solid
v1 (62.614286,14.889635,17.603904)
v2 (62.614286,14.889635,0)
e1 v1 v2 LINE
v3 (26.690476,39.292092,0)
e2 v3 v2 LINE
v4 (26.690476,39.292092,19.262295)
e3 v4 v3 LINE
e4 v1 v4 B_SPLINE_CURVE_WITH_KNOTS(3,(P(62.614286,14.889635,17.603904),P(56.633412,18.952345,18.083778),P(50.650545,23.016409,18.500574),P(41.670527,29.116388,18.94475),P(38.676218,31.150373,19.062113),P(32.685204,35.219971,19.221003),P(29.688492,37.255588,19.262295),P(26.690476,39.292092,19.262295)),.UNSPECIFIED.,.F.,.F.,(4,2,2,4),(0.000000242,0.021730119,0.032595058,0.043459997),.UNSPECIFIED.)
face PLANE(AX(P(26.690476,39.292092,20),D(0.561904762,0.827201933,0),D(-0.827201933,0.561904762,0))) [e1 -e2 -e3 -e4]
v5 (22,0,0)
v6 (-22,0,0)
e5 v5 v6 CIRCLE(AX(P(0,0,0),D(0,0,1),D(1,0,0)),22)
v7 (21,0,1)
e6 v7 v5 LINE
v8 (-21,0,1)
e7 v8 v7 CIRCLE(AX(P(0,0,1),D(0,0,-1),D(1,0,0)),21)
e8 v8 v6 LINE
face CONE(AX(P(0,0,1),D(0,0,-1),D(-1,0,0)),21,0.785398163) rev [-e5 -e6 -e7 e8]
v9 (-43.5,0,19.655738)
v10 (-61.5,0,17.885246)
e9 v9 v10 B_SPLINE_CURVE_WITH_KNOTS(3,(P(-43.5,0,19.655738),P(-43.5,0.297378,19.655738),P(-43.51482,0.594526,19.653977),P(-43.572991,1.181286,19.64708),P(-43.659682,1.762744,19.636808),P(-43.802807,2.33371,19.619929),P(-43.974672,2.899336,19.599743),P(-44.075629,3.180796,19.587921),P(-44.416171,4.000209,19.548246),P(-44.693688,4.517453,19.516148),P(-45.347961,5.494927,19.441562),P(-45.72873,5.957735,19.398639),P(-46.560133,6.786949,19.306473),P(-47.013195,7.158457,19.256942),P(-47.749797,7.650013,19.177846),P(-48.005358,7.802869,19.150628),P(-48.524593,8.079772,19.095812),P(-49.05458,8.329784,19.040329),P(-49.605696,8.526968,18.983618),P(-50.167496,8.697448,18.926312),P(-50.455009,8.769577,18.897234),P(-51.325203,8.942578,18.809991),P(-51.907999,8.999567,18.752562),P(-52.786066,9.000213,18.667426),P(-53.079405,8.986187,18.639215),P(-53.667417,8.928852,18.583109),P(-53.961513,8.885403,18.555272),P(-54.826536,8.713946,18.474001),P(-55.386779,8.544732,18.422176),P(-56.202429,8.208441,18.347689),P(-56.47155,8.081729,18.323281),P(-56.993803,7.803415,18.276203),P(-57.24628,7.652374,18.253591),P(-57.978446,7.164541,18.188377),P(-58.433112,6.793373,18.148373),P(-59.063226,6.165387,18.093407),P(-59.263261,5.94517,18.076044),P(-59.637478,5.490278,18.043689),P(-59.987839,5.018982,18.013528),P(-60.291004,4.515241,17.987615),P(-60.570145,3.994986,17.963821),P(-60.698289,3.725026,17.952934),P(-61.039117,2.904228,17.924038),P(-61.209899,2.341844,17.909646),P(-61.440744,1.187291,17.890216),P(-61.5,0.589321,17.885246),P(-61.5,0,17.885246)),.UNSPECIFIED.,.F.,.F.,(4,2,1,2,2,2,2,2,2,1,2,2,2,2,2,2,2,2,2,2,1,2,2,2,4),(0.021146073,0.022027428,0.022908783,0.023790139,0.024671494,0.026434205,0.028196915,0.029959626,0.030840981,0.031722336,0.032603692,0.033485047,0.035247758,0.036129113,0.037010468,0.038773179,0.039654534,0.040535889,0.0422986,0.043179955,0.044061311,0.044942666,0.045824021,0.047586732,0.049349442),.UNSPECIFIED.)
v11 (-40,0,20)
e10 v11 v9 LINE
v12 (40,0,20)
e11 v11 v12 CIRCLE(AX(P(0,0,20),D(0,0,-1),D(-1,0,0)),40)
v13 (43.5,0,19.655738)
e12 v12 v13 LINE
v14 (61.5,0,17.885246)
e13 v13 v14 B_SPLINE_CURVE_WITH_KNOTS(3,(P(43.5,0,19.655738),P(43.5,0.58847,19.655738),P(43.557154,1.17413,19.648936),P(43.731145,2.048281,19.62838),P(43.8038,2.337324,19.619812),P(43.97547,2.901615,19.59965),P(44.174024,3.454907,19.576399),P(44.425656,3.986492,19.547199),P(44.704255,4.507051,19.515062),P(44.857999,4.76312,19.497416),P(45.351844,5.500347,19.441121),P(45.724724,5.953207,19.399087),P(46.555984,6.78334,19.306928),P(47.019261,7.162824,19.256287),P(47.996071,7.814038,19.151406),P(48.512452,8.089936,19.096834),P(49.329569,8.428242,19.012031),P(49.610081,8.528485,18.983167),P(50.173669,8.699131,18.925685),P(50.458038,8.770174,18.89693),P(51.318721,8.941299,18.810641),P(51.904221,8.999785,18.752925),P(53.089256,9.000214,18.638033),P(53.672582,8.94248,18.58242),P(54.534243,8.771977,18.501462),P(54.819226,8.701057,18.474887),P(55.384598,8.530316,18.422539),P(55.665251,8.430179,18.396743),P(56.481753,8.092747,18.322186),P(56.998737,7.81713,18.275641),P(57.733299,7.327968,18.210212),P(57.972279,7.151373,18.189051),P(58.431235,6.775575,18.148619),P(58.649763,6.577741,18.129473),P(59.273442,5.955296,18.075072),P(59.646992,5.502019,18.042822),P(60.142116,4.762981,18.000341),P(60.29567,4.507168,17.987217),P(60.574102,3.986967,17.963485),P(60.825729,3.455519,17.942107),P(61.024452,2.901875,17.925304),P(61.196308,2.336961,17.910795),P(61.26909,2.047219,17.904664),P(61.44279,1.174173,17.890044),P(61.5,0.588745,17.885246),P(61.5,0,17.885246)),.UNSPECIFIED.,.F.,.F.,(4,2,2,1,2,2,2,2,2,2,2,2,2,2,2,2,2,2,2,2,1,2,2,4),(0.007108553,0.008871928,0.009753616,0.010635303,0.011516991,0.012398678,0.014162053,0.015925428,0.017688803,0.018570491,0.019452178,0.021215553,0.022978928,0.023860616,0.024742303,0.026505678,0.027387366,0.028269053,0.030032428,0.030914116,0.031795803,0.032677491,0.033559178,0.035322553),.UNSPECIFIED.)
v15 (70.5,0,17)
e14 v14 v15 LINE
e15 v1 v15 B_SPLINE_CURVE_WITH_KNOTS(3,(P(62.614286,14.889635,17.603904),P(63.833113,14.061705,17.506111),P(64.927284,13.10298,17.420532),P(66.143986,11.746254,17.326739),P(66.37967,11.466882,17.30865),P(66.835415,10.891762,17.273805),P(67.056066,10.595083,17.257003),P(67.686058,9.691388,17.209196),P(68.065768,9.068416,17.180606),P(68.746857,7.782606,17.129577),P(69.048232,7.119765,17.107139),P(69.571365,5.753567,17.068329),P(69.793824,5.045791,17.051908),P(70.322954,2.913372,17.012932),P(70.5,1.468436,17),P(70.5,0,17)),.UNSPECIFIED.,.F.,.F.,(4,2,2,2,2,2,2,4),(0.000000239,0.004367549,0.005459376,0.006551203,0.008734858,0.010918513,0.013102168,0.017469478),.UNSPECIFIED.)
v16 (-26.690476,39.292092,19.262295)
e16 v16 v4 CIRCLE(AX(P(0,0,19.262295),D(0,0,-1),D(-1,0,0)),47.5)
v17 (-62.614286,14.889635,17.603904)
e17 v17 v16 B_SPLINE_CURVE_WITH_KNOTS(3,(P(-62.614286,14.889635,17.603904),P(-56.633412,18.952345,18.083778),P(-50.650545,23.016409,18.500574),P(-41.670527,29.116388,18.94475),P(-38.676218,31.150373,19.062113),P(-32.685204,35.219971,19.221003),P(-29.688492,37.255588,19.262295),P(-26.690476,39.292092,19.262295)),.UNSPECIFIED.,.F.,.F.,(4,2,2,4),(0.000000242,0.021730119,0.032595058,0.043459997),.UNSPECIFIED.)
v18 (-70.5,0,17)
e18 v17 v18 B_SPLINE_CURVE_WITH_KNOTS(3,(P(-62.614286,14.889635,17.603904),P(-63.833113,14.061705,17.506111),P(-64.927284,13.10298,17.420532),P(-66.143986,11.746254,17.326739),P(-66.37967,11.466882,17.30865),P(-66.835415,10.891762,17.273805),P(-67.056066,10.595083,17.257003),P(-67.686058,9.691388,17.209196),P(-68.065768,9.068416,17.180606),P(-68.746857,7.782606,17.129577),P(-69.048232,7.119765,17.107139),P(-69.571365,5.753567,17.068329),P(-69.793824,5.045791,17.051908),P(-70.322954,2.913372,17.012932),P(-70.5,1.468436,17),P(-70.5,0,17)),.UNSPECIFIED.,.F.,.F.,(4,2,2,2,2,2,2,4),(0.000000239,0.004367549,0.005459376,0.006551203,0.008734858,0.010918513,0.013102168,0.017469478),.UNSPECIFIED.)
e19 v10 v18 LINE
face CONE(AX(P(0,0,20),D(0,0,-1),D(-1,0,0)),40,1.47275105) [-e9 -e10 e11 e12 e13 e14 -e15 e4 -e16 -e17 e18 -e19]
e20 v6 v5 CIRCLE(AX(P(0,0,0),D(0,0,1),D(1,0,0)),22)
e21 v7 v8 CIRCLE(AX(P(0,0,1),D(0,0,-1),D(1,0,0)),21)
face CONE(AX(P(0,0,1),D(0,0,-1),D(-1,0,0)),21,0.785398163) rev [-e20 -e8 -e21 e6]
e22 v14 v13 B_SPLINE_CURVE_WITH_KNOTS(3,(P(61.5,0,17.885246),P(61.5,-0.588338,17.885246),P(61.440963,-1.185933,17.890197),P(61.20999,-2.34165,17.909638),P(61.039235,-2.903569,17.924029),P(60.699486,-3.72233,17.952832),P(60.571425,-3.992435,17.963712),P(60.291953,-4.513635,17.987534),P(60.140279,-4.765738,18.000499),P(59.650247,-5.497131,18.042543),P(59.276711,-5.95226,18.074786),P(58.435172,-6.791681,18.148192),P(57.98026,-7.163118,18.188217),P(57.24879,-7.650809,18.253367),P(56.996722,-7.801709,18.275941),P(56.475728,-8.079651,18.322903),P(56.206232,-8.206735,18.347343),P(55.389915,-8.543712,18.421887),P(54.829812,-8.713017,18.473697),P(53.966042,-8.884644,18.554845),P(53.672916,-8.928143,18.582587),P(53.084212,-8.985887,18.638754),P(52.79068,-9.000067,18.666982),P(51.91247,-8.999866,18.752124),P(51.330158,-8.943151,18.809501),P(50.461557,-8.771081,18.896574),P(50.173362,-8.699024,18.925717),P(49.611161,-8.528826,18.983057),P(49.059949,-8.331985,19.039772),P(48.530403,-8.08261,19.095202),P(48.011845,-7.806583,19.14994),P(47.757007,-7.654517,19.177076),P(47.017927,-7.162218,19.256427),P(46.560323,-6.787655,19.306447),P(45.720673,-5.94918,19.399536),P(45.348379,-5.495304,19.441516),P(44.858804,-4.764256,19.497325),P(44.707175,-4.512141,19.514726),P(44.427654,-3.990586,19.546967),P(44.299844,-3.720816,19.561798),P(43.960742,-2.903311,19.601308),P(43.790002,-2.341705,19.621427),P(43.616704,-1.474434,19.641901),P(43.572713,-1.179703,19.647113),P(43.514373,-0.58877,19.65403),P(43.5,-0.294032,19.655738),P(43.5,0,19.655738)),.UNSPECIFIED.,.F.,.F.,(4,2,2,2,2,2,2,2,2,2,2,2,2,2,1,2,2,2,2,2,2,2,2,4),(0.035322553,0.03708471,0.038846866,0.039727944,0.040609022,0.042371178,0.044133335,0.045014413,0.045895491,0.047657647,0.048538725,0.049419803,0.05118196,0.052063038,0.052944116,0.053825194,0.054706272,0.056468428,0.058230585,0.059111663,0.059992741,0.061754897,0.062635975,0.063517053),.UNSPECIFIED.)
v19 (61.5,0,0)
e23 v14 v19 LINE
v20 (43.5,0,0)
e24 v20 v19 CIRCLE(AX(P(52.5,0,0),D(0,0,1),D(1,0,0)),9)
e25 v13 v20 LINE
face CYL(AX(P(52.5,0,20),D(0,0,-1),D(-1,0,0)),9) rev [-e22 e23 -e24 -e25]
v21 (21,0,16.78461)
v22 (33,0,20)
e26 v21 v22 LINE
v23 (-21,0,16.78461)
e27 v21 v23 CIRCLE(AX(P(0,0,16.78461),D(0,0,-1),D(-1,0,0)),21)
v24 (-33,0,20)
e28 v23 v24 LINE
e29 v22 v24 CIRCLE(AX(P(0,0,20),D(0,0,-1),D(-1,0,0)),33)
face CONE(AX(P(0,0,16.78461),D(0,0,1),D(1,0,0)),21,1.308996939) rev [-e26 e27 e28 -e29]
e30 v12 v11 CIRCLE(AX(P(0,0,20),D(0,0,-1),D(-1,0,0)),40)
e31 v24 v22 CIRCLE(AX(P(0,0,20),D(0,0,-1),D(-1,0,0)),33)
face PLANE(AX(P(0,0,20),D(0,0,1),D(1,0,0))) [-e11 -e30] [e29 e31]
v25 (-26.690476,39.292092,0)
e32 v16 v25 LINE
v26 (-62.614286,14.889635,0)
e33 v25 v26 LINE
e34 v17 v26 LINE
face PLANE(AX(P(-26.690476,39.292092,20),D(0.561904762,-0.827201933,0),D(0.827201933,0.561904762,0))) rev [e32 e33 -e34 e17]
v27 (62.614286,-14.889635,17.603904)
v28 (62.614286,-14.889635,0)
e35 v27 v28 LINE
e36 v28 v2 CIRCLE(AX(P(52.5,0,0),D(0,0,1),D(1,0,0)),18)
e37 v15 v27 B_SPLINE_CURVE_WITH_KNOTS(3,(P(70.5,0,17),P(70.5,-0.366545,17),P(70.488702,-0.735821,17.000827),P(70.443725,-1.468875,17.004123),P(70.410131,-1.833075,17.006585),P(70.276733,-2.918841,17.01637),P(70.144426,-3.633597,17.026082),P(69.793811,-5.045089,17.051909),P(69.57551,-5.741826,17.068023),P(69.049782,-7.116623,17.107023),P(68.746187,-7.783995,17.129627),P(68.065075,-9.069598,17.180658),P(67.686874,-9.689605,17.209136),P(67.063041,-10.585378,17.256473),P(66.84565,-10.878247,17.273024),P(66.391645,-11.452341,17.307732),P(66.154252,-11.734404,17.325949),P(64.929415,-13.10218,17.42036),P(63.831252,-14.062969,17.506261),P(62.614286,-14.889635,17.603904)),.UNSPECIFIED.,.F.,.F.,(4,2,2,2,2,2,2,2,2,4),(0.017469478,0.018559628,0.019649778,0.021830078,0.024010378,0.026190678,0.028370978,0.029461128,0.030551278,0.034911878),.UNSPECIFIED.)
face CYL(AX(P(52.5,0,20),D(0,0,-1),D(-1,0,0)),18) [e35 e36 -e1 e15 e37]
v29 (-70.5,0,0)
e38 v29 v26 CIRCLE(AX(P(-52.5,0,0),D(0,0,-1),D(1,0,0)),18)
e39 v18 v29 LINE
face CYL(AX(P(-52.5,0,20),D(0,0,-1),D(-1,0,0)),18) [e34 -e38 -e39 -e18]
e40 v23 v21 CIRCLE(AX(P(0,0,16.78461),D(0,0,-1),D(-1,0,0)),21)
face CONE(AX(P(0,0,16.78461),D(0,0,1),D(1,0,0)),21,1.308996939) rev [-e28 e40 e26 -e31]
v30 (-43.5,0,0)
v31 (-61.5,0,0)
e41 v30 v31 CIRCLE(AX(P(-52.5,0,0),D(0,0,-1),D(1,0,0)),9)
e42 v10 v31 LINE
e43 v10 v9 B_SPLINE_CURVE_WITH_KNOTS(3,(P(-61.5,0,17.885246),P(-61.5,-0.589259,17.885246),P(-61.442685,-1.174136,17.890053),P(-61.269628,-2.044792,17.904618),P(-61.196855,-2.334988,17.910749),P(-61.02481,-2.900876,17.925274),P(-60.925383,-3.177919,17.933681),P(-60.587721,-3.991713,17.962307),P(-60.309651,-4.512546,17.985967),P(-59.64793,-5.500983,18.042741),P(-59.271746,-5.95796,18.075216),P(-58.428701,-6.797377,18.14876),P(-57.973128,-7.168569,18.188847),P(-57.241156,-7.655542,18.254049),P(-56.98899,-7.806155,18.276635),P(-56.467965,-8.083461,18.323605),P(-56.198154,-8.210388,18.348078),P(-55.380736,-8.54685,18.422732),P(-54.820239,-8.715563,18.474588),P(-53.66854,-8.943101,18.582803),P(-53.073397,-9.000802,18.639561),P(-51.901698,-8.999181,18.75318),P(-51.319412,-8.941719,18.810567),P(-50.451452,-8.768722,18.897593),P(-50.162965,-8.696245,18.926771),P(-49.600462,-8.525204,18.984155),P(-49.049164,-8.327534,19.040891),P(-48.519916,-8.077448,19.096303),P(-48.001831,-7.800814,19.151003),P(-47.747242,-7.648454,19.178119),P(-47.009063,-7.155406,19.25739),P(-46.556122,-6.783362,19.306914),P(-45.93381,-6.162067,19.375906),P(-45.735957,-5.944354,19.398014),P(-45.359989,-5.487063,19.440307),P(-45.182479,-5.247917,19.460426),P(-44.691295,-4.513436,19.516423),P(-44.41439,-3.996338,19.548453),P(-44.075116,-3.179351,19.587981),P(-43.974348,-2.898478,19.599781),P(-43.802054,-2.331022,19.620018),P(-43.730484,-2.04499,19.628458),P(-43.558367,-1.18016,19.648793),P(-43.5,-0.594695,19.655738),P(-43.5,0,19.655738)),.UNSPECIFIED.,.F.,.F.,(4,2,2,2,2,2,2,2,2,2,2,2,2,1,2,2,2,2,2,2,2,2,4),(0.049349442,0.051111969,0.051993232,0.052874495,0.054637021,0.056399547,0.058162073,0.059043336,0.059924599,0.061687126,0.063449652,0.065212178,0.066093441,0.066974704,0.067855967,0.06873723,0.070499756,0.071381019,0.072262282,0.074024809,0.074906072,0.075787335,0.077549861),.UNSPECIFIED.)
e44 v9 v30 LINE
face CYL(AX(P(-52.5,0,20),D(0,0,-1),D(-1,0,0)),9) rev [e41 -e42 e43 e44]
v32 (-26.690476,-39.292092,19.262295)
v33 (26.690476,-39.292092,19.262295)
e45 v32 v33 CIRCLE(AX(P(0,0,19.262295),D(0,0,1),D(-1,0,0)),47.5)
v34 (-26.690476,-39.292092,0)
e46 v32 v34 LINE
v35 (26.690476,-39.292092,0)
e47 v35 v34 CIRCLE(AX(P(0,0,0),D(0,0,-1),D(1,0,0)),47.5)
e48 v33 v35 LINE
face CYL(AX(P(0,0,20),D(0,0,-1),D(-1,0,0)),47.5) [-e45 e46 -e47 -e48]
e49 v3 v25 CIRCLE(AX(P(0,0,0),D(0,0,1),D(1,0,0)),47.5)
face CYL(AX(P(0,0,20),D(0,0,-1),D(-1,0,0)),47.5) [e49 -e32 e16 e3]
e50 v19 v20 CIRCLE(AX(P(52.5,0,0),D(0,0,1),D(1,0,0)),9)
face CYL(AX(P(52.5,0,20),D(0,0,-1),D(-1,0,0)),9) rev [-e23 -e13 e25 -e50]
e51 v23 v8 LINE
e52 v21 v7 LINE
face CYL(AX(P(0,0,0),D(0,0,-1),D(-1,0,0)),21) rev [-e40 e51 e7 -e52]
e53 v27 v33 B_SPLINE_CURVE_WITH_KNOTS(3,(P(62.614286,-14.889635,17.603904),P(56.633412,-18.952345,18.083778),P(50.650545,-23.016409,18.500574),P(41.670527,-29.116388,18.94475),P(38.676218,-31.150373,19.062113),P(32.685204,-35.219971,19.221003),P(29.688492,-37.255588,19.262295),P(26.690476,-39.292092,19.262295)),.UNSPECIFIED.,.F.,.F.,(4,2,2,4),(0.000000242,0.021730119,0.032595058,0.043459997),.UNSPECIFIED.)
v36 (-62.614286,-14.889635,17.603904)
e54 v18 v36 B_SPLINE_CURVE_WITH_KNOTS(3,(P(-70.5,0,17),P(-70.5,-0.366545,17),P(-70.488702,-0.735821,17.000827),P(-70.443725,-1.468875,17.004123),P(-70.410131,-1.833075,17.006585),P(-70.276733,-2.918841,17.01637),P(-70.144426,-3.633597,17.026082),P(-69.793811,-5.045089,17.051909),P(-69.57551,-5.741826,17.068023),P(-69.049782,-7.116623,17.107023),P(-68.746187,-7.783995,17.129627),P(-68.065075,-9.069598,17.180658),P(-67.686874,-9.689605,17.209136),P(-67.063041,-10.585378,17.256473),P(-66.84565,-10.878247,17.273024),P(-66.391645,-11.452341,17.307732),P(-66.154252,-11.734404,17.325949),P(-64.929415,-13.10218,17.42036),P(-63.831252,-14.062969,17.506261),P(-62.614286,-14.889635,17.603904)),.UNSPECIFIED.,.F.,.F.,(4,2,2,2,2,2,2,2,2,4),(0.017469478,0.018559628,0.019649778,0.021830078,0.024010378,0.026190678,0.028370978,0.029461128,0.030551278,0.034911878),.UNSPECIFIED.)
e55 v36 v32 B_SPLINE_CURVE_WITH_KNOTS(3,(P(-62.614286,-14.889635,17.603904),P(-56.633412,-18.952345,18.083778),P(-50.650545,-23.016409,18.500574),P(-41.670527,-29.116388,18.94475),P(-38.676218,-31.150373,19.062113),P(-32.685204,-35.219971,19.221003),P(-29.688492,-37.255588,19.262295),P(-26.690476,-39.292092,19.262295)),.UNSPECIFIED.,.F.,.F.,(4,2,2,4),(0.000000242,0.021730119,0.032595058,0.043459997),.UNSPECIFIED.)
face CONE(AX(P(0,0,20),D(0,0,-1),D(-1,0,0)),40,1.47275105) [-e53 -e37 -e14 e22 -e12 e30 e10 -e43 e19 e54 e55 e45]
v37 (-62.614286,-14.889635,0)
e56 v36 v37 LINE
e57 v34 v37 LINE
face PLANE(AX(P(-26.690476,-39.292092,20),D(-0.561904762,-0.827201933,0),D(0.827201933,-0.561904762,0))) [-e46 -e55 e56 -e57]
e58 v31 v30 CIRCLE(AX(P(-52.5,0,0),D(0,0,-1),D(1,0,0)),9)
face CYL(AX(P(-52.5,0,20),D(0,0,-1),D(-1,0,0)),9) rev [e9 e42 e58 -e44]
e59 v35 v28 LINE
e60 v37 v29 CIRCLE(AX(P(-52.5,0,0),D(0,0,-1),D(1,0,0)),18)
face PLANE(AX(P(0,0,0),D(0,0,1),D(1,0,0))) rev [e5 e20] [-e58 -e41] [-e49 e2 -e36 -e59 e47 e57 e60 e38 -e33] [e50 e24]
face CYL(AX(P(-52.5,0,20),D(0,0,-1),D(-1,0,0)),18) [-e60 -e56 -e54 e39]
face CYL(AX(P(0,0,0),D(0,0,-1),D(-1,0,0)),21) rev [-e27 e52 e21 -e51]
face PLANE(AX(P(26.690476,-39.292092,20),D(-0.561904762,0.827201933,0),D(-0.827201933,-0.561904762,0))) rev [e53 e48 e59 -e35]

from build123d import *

# Parameters (mm, degrees)
SKETCH1_R           = 9
BOSS_EXTRUDE1_DEPTH = 20
SKETCH5_W           = 21
SKETCH5_H           = 16.784609691
CHAMFER1_SIZE       = 1


with BuildPart() as part:
    # Sketch1 → Boss-Extrude1 (new body)
    with BuildSketch(Plane.XY):
        with BuildLine():
            Line((26.69047619, 39.292091834), (62.614285714, 14.8896348))
            ThreePointArc((62.614285714, 14.8896348), (70.5, 0), (62.614285714, -14.8896348))
            Line((62.614285714, -14.8896348), (26.69047619, -39.292091834))
            ThreePointArc((26.69047619, -39.292091834), (0, -47.5), (-26.69047619, -39.292091834))
            Line((-26.69047619, -39.292091834), (-62.614285714, -14.8896348))
            ThreePointArc((-62.614285714, -14.8896348), (-70.5, 0), (-62.614285714, 14.8896348))
            Line((-62.614285714, 14.8896348), (-26.69047619, 39.292091834))
            ThreePointArc((-26.69047619, 39.292091834), (0, 47.5), (26.69047619, 39.292091834))
        make_face()
        with Locations((52.5, 0)):
            Circle(SKETCH1_R, mode=Mode.SUBTRACT)
        with Locations((-52.5, 0)):
            Circle(SKETCH1_R, mode=Mode.SUBTRACT)
    extrude(amount=BOSS_EXTRUDE1_DEPTH)

    # Sketch5 → Cut-Revolve1 (revolve, cut)
    with BuildSketch(Plane(origin=(0, 0, 0), x_dir=(1, 0, 0), z_dir=(0, 1, 0)), mode=Mode.PRIVATE) as cut_revolve1_sk:
        with Locations((10.5, -8.392304845)):
            Rectangle(SKETCH5_W, SKETCH5_H)
        Polygon((21, -16.784609691), (33, -20), (0, -20), (0, -16.784609691), align=None)
        Polygon((40, -20), (70.5, -20), (70.5, -17), align=None)
    revolve(cut_revolve1_sk.sketch.rotate(Axis((0, 0, 0), (0, 0, 1)), 180), axis=Axis((0, 0, 0), (0, 0, 1)), mode=Mode.SUBTRACT)

    # Chamfer1
    chamfer1_edges = [part.edges().sort_by_distance(p)[0] for p in [
        (21, 0, 0),
    ]]
    chamfer(chamfer1_edges, length=CHAMFER1_SIZE)


solid = part.part
